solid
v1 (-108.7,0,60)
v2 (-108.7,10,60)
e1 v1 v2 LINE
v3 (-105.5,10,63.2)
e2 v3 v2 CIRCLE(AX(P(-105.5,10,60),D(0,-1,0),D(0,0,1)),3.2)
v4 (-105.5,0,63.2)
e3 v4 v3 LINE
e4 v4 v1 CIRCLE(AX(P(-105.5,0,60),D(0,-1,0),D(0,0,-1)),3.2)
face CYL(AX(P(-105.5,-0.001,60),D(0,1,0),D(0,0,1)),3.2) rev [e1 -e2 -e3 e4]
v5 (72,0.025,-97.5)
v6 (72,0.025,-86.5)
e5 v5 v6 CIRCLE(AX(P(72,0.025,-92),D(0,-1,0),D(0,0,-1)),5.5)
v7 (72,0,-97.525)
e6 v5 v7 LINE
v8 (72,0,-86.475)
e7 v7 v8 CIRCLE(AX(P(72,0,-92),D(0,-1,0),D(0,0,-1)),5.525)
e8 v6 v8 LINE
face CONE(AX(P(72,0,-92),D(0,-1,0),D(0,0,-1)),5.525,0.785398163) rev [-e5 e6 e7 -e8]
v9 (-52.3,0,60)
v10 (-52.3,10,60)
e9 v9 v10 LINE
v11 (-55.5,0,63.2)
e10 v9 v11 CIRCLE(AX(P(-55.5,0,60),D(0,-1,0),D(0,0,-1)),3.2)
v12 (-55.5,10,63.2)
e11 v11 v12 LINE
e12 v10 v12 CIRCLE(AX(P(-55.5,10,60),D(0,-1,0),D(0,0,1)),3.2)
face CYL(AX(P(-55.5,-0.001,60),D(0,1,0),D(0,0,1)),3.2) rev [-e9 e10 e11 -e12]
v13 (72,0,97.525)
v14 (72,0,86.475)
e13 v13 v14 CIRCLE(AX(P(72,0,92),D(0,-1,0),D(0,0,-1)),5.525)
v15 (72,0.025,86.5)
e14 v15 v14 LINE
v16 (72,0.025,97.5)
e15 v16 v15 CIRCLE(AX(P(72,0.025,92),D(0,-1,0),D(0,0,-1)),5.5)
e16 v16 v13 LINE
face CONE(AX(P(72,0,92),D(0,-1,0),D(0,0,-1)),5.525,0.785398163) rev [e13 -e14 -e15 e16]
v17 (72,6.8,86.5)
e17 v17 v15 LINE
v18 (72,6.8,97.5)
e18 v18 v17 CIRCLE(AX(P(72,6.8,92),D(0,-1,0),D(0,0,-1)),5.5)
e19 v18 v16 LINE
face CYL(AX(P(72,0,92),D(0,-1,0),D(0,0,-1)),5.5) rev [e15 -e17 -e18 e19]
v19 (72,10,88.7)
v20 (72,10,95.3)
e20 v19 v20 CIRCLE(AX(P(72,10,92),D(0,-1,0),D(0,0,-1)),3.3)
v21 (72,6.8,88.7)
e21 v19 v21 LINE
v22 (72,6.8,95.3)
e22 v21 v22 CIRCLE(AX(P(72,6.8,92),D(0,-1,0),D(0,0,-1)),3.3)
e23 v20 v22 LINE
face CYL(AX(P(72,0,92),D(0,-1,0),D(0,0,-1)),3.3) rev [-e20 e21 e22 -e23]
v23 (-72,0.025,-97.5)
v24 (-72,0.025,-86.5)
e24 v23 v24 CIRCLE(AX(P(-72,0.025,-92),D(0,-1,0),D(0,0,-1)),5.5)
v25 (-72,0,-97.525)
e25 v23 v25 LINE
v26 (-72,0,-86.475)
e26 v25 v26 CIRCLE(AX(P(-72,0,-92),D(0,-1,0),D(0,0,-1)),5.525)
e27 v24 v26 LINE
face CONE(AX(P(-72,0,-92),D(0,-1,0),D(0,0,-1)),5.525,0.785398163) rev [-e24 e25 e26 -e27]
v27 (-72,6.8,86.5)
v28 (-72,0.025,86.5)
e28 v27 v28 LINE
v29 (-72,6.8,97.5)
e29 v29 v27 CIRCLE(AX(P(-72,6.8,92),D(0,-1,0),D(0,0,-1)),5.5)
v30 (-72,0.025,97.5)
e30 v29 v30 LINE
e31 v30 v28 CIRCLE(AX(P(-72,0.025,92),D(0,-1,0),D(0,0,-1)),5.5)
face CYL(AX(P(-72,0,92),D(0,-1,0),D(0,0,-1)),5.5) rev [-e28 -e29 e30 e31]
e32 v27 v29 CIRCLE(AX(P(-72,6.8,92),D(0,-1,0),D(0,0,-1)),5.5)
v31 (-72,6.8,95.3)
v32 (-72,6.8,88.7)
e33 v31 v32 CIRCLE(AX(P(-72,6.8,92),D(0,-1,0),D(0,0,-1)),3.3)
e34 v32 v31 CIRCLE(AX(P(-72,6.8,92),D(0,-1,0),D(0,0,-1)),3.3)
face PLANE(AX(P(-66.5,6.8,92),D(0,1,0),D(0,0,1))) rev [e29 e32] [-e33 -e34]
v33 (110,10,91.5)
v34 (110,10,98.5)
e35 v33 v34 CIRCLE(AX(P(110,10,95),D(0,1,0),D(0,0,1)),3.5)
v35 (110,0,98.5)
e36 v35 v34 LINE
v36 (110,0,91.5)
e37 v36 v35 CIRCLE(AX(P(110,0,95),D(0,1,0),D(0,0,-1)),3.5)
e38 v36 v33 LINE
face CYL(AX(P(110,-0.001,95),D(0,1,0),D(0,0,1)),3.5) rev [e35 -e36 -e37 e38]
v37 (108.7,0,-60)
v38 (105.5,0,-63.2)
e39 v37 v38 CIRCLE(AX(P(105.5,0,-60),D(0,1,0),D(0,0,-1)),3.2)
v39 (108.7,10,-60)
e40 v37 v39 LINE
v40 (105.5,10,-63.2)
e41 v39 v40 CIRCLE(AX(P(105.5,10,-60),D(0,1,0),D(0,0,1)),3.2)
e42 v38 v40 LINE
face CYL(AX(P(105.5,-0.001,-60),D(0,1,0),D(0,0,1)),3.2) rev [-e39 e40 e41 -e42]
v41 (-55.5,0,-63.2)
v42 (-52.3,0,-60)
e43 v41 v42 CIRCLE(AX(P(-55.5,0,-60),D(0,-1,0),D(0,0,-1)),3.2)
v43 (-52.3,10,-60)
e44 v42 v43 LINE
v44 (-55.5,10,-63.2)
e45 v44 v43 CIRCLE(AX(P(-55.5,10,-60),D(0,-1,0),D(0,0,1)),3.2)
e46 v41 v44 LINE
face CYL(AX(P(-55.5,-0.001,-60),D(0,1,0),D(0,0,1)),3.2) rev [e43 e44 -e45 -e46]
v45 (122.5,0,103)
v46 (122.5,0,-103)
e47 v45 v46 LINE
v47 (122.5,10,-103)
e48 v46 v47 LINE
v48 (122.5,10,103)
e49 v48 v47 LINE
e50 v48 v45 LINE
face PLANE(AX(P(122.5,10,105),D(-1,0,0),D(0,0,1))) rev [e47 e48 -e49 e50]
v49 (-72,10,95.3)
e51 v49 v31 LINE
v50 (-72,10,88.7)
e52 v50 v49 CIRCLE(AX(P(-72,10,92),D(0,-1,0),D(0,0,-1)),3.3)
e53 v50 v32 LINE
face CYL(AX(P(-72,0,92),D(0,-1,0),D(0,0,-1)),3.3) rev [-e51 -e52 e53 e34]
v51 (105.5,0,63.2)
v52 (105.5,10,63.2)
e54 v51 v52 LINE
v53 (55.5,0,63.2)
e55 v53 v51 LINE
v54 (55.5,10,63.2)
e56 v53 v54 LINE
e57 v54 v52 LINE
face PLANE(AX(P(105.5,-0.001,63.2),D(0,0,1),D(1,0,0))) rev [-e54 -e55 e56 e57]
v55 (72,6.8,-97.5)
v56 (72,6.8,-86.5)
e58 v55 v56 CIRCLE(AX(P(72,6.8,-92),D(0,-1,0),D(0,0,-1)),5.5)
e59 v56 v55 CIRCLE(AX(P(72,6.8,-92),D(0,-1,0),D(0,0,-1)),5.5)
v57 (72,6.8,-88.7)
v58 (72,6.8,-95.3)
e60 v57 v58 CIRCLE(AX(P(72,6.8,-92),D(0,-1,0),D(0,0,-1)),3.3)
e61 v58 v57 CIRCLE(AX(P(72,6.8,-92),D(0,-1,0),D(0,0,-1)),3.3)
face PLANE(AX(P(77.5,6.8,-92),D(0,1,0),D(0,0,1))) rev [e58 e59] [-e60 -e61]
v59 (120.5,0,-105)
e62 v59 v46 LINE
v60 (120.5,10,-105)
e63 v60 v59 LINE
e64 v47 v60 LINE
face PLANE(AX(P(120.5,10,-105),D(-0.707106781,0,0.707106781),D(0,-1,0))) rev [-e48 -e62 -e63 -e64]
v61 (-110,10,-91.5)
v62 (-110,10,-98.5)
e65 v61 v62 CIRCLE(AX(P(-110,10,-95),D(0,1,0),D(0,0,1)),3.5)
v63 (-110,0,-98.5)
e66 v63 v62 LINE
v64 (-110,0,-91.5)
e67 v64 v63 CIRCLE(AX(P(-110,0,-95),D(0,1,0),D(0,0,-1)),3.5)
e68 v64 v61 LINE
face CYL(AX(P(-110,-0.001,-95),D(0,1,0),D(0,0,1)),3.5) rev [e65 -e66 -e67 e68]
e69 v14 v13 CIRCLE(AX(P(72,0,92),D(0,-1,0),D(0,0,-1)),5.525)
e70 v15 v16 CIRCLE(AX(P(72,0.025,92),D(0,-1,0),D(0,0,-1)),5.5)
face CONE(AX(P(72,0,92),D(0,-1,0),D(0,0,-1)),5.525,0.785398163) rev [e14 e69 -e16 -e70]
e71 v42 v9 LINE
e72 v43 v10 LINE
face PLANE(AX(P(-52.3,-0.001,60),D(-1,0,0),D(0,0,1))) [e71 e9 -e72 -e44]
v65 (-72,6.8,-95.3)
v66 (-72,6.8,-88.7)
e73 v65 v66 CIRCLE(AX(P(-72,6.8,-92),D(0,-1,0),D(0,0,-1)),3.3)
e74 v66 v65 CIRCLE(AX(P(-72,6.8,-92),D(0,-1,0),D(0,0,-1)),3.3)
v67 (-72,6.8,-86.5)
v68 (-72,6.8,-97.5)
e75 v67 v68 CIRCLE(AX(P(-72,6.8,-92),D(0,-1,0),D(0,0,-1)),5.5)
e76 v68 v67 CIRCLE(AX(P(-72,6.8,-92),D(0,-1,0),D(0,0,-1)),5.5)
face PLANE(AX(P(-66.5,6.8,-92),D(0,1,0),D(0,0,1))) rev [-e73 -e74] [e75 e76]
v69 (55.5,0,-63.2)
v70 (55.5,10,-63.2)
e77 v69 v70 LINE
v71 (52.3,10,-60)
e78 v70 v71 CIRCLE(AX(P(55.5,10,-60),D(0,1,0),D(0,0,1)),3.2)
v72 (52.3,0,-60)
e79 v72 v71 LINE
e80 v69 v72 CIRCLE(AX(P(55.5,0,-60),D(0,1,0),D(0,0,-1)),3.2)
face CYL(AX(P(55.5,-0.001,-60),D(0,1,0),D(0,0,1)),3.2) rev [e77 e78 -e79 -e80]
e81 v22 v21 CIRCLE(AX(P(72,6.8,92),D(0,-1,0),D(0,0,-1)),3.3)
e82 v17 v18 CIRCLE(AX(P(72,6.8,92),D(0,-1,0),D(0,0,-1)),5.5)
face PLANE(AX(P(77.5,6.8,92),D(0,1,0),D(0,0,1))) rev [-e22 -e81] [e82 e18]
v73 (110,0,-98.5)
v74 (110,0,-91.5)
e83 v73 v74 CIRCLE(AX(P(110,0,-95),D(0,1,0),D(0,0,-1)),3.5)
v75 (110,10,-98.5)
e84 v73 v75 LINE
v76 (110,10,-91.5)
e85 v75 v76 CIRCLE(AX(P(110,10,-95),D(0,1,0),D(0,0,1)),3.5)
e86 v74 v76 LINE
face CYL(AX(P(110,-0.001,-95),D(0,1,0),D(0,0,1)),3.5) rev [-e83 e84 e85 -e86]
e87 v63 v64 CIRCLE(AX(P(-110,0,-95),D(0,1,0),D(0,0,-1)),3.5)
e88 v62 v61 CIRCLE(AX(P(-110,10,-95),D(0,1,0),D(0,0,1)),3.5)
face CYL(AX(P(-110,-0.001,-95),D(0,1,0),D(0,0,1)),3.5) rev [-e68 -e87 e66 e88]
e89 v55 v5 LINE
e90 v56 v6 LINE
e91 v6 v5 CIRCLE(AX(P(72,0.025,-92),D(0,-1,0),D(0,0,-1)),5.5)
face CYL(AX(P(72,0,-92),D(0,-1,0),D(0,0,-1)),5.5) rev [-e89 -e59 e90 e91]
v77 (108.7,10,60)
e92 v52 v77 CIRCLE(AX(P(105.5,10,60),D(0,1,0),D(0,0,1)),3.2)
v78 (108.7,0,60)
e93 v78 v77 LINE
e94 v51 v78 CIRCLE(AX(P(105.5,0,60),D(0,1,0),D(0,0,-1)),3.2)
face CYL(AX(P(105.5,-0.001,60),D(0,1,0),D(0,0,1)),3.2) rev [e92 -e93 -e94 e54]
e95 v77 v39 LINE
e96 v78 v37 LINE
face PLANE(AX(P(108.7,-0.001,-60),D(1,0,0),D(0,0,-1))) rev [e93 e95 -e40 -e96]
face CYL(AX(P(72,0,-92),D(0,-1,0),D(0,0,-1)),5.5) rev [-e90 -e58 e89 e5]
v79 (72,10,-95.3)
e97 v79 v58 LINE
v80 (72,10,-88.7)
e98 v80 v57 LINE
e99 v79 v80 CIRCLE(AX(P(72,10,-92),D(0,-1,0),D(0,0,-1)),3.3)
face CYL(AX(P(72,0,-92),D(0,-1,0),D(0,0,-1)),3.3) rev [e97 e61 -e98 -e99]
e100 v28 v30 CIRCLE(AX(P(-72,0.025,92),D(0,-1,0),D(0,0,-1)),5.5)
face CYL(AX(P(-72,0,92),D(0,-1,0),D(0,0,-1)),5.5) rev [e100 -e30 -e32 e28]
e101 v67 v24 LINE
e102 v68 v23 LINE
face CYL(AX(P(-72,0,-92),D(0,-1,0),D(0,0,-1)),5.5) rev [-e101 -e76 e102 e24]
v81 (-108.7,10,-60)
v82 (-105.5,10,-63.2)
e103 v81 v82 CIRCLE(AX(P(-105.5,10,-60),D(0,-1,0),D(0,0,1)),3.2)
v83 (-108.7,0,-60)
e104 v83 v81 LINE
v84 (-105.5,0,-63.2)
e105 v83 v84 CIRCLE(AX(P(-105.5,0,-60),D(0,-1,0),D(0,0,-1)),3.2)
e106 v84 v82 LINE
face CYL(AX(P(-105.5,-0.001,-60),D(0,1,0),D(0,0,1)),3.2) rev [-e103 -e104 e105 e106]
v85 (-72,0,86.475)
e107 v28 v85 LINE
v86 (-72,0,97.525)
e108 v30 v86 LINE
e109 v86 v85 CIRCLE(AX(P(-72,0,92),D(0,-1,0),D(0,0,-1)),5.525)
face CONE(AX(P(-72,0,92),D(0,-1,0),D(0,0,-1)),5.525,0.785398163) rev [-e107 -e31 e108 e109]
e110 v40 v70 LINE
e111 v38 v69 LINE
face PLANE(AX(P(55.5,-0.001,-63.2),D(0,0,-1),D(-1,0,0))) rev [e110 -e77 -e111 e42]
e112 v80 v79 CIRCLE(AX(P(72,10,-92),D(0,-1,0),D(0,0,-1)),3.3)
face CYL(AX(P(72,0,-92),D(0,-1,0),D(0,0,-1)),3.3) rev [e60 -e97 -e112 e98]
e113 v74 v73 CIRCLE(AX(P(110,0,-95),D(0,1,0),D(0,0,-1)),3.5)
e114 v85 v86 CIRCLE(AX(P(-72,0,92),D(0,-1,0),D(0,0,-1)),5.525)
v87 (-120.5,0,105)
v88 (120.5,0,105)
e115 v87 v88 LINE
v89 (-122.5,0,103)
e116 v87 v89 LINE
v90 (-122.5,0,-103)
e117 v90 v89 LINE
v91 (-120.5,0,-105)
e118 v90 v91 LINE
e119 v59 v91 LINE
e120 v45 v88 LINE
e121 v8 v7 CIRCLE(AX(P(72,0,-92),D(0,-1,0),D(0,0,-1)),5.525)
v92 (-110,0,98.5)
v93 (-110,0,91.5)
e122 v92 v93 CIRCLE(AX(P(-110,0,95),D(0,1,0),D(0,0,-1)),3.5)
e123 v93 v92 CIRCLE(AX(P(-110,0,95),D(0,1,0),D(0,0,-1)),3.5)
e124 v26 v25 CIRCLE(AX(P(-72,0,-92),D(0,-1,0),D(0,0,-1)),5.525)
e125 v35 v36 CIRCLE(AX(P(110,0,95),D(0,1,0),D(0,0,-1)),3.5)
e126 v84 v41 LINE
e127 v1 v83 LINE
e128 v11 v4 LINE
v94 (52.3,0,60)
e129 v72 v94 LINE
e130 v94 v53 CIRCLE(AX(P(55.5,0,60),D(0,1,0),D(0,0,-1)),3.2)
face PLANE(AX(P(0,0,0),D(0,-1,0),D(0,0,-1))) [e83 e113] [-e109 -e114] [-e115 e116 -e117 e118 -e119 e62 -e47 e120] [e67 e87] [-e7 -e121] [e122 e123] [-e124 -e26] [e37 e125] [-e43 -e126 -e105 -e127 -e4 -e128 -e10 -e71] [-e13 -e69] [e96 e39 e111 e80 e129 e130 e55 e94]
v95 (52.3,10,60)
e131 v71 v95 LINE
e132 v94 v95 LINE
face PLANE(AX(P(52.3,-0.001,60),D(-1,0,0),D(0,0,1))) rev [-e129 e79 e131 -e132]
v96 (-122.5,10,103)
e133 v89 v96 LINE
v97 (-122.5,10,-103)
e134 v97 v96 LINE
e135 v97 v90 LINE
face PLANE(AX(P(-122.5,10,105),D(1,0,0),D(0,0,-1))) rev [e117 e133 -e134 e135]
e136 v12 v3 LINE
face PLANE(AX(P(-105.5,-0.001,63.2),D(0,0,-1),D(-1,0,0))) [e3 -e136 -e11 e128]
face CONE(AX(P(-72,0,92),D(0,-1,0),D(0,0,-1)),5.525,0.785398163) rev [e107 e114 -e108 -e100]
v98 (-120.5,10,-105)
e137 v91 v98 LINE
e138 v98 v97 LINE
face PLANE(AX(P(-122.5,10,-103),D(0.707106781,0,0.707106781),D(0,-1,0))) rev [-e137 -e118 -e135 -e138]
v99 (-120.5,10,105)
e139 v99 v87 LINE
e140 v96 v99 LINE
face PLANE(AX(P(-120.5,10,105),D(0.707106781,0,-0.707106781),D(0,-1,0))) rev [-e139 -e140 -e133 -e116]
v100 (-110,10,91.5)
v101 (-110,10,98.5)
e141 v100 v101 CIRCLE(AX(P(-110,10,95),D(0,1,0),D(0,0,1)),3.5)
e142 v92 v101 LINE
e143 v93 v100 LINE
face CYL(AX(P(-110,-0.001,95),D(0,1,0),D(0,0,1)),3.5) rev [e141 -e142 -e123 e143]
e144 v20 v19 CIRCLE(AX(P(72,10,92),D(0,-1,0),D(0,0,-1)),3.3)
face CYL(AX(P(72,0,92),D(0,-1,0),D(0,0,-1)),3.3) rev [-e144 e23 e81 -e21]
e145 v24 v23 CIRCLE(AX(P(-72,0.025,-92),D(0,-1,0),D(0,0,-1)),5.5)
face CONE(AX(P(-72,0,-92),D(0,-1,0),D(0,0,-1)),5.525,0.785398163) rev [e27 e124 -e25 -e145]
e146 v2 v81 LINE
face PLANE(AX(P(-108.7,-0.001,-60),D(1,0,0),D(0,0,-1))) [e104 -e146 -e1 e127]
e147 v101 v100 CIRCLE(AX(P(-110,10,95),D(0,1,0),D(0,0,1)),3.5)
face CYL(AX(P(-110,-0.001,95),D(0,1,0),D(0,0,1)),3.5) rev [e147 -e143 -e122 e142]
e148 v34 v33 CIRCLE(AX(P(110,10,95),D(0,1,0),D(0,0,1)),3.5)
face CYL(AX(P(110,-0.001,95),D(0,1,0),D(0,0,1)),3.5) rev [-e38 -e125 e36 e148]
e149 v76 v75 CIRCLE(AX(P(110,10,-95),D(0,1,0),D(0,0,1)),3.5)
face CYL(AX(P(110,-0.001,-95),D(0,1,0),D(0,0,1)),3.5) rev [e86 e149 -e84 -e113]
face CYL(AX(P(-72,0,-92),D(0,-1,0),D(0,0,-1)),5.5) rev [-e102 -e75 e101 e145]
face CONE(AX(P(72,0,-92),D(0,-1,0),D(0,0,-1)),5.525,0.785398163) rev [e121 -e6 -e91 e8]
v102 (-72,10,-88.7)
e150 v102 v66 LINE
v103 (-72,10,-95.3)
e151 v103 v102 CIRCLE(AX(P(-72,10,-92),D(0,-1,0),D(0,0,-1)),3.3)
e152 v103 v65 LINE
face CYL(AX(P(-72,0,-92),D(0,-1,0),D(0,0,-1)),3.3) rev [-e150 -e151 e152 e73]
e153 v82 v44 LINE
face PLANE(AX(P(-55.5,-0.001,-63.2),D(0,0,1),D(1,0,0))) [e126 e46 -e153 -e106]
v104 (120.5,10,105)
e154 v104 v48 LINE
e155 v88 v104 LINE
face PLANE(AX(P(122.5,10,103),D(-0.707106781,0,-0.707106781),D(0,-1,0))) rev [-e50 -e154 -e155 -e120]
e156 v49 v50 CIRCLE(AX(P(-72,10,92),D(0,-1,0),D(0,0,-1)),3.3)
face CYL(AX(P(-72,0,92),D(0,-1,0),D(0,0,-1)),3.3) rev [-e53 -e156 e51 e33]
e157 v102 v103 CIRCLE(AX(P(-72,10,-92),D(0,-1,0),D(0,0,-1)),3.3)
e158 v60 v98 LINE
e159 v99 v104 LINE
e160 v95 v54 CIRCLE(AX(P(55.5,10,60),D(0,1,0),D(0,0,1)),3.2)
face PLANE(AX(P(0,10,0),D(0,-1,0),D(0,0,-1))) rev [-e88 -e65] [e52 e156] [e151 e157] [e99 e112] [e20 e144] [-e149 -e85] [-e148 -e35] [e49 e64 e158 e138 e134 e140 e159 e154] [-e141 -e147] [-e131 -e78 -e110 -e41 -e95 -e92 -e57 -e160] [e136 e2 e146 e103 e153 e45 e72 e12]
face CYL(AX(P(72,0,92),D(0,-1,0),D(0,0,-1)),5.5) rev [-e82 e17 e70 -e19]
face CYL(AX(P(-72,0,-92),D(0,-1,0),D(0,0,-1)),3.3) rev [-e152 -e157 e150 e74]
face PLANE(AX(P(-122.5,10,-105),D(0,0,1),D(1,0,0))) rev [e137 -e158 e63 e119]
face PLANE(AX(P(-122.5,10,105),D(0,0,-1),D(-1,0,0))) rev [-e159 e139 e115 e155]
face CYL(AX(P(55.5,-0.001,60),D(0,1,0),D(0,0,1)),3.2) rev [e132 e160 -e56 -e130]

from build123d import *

# Parameters (mm, degrees)
SKETCH_1_W          = 245
SKETCH_1_H          = 210
EXTRUDE_1_DEPTH     = 10
CHAMFER_1_SIZE      = 2
CUT_EXTRUDE_1_REACH = 163.652
SKETCH_5_R          = 3.5
CUT_EXTRUDE_2_REACH = 163.652


with BuildPart() as part:
    # 草图1 → 凸台-拉伸1 (new body)
    with BuildSketch(Plane(origin=(0, 0, 0), x_dir=(1, 0, 0), z_dir=(0, 1, 0))):
        Rectangle(SKETCH_1_W, SKETCH_1_H)
    extrude(amount=EXTRUDE_1_DEPTH)

    # 倒角1
    chamfer_1_edges = [part.edges().sort_by_distance(p)[0] for p in [
        (122.5, 5, 105),
        (-122.5, 5, 105),
        (-122.5, 5, -105),
        (122.5, 5, -105),
    ]]
    chamfer(chamfer_1_edges, length=CHAMFER_1_SIZE)

    # 草图4 → 打孔尺寸(%根据)内六角圆柱头螺钉的类型1 (revolve, cut)
    with BuildSketch(Plane(origin=(72, 0, 92), x_dir=(0, 0, -1), z_dir=(1, 0, 0))):
        Polygon((0, 0), (0, 10.001), (3.3, 10.001), (3.3, 6.8), (5.5, 6.8), (5.5, 0.025), (5.525, 0), align=None)
    hole_wizard_1 = revolve(axis=Axis((72, -6.35, 92), (0, 1, 0)), mode=Mode.SUBTRACT)

    # 镜向1: 打孔尺寸(%根据)内六角圆柱头螺钉的类型1 across plane
    add(hole_wizard_1.mirror(Plane(origin=(0, 0, 0), x_dir=(0, 0, 1), z_dir=(1, 0, 0))), mode=Mode.SUBTRACT)

    # 镜向2: 打孔尺寸(%根据)内六角圆柱头螺钉的类型1 across plane
    add(hole_wizard_1.mirror(Plane.XY), mode=Mode.SUBTRACT)

    # 镜向2 copy 1 sketch → 镜向2 copy 1 (revolve, cut)
    with BuildSketch(Plane(origin=(-72, 0, -92), x_dir=(0, 0, 1), z_dir=(-1, 0, 0))):
        Polygon((0, 0), (0, 10.001), (3.3, 10.001), (3.3, 6.8), (5.5, 6.8), (5.5, 0.025), (5.525, 0), align=None)
    revolve(axis=Axis((-72, -6.35, -92), (0, 1, 0)), mode=Mode.SUBTRACT)

    # 草图5 → 切除-拉伸1 (cut, up to next)
    with BuildSketch(Plane(origin=(0, 10, 0), x_dir=(1, 0, 0), z_dir=(0, 1, 0)), mode=Mode.PRIVATE) as cut_extrude_1_sk1:
        with Locations(Location((-110, 95, 0), (0, 0, 270))):
            Circle(SKETCH_5_R)
    cut_extrude_1_tool1 = extrude(cut_extrude_1_sk1.sketch, amount=-CUT_EXTRUDE_1_REACH, mode=Mode.PRIVATE) & part.part
    # 草图5 → 切除-拉伸1 (cut, up to next)
    with BuildSketch(Plane(origin=(0, 10, 0), x_dir=(1, 0, 0), z_dir=(0, 1, 0)), mode=Mode.PRIVATE) as cut_extrude_1_sk2:
        with Locations(Location((110, 95, 0), (0, 0, 270))):
            Circle(SKETCH_5_R)
    cut_extrude_1_tool2 = extrude(cut_extrude_1_sk2.sketch, amount=-CUT_EXTRUDE_1_REACH, mode=Mode.PRIVATE) & part.part
    # 草图5 → 切除-拉伸1 (cut, up to next)
    with BuildSketch(Plane(origin=(0, 10, 0), x_dir=(1, 0, 0), z_dir=(0, 1, 0)), mode=Mode.PRIVATE) as cut_extrude_1_sk3:
        with Locations(Location((110, -95, 0), (0, 0, 270))):
            Circle(SKETCH_5_R)
    cut_extrude_1_tool3 = extrude(cut_extrude_1_sk3.sketch, amount=-CUT_EXTRUDE_1_REACH, mode=Mode.PRIVATE) & part.part
    # 草图5 → 切除-拉伸1 (cut, up to next)
    with BuildSketch(Plane(origin=(0, 10, 0), x_dir=(1, 0, 0), z_dir=(0, 1, 0)), mode=Mode.PRIVATE) as cut_extrude_1_sk4:
        with Locations(Location((-110, -95, 0), (0, 0, 270))):
            Circle(SKETCH_5_R)
    cut_extrude_1_tool4 = extrude(cut_extrude_1_sk4.sketch, amount=-CUT_EXTRUDE_1_REACH, mode=Mode.PRIVATE) & part.part
    add(cut_extrude_1_tool1.solids().sort_by_distance((-110, 10, -95))[0], mode=Mode.SUBTRACT)
    add(cut_extrude_1_tool2.solids().sort_by_distance((110, 10, -95))[0], mode=Mode.SUBTRACT)
    add(cut_extrude_1_tool3.solids().sort_by_distance((110, 10, 95))[0], mode=Mode.SUBTRACT)
    add(cut_extrude_1_tool4.solids().sort_by_distance((-110, 10, 95))[0], mode=Mode.SUBTRACT)

    # 草图6 → 切除-拉伸2 (cut, up to next)
    with BuildSketch(Plane(origin=(0, 10, 0), x_dir=(1, 0, 0), z_dir=(0, 1, 0)), mode=Mode.PRIVATE) as cut_extrude_2_sk1:
        with BuildLine():
            Line((105.5, -63.2), (55.5, -63.2))
            ThreePointArc((55.5, -63.2), (53.2372583, -62.2627417), (52.3, -60))
            Line((52.3, -60), (52.3, 60))
            ThreePointArc((52.3, 60), (53.2372583, 62.2627417), (55.5, 63.2))
            Line((55.5, 63.2), (105.5, 63.2))
            ThreePointArc((105.5, 63.2), (107.7627417, 62.2627417), (108.7, 60))
            Line((108.7, 60), (108.7, -60))
            ThreePointArc((108.7, -60), (107.7627417, -62.2627417), (105.5, -63.2))
        make_face()
    cut_extrude_2_tool1 = extrude(cut_extrude_2_sk1.sketch, amount=-CUT_EXTRUDE_2_REACH, mode=Mode.PRIVATE) & part.part
    cut_extrude_2 = cut_extrude_2_tool1.solids().sort_by_distance((80.5, 10, 0))[0]
    add(cut_extrude_2, mode=Mode.SUBTRACT)

    # 镜向3: 切除-拉伸2 across plane
    add(cut_extrude_2.mirror(Plane(origin=(0, 0, 0), x_dir=(0, 0, 1), z_dir=(1, 0, 0))), mode=Mode.SUBTRACT)


solid = part.part
